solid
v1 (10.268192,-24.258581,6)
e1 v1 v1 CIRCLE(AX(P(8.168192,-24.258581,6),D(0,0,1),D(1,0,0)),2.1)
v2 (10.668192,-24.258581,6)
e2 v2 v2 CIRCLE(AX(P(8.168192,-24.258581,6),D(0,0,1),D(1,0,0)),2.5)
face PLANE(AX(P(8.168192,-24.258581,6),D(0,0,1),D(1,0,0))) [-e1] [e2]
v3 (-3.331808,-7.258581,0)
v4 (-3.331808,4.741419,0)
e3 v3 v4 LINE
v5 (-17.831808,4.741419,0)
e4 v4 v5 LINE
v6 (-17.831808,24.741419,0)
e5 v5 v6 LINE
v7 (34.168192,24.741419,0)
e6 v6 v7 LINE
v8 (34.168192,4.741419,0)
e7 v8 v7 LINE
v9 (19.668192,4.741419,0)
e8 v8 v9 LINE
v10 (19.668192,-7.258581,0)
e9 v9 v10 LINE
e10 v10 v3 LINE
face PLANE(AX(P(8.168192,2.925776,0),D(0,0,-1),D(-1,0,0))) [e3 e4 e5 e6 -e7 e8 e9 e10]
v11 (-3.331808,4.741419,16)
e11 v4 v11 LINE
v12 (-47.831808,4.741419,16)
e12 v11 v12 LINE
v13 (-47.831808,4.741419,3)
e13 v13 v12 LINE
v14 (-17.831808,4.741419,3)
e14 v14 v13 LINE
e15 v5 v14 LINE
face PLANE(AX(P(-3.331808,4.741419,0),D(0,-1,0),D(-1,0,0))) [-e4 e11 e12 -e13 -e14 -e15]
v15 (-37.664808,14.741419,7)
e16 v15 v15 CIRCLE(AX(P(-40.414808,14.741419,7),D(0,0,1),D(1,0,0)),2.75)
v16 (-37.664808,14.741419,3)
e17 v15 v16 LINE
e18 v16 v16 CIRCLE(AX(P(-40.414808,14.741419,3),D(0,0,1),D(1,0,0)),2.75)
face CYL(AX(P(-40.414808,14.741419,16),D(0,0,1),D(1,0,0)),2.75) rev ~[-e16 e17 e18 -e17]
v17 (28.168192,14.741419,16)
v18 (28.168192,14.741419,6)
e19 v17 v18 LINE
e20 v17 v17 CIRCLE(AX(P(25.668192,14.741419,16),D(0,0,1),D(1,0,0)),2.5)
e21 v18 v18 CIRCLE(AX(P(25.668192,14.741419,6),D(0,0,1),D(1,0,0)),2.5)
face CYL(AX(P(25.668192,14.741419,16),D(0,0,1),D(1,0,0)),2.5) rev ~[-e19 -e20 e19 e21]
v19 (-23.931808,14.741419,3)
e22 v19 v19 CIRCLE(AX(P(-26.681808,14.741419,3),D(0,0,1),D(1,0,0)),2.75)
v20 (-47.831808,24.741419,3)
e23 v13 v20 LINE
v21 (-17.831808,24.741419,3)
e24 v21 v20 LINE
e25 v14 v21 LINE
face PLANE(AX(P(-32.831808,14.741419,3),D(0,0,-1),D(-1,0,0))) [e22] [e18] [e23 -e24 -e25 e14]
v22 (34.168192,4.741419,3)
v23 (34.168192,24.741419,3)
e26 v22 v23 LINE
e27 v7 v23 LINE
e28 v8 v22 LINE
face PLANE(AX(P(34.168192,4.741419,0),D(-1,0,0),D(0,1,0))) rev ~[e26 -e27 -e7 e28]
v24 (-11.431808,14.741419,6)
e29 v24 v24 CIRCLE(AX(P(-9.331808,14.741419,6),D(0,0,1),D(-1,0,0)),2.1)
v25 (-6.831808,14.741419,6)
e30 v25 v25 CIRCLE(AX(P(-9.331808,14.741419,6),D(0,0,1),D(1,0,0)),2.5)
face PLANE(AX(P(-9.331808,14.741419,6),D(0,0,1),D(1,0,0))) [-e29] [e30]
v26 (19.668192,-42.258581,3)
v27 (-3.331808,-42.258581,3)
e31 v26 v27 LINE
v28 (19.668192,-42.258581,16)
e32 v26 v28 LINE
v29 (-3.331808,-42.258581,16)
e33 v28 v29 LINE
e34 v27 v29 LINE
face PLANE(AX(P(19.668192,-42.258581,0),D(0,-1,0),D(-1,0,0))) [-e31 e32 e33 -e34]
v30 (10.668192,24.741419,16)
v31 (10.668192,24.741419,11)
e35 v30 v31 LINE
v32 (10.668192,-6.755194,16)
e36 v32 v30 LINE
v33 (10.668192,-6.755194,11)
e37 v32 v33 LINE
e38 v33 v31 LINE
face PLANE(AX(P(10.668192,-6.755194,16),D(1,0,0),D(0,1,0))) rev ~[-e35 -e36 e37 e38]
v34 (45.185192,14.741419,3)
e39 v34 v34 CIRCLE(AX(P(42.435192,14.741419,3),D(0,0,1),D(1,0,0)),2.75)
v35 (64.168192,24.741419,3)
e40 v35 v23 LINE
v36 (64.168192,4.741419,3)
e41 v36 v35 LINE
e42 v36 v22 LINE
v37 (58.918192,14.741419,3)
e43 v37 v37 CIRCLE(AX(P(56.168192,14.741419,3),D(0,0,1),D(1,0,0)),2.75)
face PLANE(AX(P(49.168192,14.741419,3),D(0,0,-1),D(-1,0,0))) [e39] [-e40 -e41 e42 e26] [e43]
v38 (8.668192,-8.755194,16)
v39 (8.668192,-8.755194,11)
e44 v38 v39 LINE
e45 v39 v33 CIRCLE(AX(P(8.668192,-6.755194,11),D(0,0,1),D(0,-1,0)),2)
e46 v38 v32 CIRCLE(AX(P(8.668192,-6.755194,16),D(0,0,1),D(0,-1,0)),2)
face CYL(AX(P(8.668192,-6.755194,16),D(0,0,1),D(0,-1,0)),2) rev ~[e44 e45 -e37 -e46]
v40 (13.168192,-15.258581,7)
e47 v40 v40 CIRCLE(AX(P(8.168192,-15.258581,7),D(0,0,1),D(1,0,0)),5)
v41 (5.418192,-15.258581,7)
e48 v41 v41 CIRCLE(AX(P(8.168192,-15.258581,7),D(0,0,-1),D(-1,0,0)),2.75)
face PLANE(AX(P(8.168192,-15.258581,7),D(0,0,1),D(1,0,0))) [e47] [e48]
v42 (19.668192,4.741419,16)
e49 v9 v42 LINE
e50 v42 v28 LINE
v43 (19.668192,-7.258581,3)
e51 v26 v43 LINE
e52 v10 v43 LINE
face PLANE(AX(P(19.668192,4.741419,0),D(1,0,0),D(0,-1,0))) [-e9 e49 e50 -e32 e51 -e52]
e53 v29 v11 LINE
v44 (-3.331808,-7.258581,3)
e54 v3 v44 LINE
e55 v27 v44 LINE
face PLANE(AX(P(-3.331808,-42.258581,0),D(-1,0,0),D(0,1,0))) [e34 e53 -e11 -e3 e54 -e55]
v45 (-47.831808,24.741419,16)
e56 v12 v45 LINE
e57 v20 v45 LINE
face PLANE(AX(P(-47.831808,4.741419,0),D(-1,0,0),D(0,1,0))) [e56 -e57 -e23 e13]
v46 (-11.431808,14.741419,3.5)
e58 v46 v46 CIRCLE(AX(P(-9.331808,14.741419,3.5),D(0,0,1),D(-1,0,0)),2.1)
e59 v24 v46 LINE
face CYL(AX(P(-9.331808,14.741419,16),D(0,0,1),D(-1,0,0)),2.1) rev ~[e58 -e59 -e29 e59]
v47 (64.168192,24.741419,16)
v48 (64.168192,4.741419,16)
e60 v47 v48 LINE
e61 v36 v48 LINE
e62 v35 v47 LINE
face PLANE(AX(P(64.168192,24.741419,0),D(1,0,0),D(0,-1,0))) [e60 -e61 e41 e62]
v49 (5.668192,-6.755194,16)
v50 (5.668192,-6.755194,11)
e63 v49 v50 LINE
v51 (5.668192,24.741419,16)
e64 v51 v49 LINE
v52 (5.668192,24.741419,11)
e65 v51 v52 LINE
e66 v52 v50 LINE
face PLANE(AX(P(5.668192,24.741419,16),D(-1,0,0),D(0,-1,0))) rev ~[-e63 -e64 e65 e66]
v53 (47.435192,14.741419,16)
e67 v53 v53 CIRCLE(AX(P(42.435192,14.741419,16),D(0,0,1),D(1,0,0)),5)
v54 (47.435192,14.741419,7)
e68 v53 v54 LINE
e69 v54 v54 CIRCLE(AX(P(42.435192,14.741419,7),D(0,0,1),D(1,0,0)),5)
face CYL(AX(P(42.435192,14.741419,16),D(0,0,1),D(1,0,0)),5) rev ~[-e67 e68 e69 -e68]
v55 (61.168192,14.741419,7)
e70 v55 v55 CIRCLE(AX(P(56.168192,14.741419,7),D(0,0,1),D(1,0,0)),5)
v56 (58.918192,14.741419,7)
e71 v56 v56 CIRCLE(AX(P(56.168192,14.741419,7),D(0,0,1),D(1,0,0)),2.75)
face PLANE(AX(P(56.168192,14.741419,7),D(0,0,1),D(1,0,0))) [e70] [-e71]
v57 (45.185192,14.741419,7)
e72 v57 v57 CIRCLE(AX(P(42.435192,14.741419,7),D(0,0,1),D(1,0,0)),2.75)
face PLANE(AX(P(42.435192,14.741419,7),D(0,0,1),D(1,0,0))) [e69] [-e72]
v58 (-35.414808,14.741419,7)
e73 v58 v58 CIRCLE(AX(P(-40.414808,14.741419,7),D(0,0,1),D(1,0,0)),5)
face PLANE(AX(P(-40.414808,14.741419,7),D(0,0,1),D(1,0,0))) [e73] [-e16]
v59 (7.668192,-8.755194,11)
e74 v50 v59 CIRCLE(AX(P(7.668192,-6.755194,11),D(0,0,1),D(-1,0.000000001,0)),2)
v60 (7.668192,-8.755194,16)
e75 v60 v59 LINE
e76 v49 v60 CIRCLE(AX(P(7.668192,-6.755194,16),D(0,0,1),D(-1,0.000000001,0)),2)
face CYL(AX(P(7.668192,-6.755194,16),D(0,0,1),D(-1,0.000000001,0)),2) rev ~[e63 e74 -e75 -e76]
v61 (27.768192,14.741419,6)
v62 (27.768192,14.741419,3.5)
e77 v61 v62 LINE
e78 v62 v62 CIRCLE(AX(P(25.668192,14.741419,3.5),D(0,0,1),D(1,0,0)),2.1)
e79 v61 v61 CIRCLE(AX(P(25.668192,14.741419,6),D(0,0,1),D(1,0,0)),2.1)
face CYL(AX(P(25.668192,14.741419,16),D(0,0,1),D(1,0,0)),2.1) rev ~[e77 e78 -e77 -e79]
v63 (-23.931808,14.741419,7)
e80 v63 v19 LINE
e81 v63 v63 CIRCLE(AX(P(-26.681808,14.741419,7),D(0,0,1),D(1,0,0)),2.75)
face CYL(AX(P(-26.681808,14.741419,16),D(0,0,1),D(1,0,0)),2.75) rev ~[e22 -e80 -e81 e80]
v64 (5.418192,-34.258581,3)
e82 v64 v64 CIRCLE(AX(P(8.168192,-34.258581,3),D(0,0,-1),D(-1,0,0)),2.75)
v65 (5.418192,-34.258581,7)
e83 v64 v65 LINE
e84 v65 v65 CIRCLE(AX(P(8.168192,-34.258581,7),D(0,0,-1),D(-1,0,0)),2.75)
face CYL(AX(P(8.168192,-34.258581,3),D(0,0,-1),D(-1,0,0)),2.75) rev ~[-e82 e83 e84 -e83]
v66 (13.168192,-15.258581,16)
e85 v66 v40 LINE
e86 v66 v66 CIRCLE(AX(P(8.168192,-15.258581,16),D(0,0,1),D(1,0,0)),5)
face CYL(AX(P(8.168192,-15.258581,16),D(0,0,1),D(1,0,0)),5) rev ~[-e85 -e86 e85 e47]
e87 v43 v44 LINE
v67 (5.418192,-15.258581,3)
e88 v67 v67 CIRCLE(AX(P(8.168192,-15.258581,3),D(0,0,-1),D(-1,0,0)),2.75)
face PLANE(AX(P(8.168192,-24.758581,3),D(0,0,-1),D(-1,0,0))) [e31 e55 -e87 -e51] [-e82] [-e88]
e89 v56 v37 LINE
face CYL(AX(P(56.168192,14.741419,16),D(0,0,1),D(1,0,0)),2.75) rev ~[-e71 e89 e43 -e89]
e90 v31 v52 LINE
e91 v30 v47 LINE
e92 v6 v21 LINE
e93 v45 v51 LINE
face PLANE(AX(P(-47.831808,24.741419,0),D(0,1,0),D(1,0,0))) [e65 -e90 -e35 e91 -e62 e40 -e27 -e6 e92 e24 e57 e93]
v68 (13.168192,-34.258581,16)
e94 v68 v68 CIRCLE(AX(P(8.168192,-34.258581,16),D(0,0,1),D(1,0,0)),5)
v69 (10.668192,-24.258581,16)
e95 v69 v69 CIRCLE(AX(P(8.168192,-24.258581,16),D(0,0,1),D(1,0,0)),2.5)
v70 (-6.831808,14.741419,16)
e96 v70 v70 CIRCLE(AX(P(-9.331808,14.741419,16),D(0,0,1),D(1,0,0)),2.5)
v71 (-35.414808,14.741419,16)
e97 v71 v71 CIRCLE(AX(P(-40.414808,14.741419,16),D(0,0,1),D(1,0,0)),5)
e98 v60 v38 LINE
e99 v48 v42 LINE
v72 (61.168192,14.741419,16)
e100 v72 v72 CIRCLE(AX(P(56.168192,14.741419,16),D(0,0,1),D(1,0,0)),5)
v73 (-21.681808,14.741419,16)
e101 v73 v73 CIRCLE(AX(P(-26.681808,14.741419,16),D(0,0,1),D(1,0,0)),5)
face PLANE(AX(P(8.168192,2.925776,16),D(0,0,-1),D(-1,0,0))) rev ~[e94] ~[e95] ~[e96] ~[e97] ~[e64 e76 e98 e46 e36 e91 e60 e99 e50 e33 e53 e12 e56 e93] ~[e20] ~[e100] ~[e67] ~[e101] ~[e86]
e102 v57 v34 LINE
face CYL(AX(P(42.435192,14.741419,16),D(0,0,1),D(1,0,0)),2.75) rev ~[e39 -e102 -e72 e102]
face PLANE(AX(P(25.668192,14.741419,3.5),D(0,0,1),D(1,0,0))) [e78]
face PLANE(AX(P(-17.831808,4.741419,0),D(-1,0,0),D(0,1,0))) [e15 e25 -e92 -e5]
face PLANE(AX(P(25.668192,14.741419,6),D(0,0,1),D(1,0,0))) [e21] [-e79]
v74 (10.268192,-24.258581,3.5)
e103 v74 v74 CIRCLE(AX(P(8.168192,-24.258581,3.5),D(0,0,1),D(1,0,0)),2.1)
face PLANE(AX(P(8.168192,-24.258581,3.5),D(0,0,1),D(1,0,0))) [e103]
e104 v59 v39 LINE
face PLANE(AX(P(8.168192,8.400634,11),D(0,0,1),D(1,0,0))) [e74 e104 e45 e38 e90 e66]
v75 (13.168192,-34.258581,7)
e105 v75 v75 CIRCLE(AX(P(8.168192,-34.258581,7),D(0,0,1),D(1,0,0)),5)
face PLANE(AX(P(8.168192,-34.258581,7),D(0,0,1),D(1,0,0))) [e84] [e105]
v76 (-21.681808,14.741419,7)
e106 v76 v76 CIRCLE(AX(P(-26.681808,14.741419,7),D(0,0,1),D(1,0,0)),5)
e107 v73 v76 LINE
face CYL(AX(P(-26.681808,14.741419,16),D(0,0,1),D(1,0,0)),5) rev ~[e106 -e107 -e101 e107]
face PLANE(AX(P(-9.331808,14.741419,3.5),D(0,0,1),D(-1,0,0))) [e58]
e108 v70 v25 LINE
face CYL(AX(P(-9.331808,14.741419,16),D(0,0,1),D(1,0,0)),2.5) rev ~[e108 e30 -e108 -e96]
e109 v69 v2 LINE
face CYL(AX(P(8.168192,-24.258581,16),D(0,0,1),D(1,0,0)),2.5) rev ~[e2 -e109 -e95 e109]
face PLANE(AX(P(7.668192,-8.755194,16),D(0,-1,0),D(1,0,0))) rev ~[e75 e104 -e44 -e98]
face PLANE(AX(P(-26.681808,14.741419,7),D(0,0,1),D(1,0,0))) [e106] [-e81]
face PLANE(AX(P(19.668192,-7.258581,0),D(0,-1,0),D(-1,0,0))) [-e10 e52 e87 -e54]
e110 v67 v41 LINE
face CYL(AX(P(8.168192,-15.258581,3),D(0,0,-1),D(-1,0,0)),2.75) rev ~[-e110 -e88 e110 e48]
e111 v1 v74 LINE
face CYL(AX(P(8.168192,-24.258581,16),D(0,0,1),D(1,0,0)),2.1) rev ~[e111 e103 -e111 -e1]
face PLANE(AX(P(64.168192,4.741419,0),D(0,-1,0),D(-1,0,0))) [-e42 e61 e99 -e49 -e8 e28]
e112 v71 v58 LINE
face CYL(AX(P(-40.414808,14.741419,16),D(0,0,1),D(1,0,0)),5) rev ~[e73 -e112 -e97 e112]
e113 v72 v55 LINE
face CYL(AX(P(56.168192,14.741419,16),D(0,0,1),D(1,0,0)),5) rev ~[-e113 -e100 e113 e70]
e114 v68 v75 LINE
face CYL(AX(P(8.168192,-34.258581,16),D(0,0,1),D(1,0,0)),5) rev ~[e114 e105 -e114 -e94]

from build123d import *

# Parameters (mm, degrees)
EXTRUDE_1_DEPTH     = 16
SKETCH_2_W          = 30
SKETCH_2_H          = 20
SKETCH_2_W_2        = 23
SKETCH_2_H_2        = 35
CUT_EXTRUDE_1_DEPTH = 3
CUT_EXTRUDE_2_DEPTH = 5
CUT_EXTRUDE_3_REACH = 80.481
SKETCH_4_R          = 2.75
CUT_EXTRUDE_4_REACH = 79.925
SKETCH_5_R          = 2.75
SKETCH_6_R          = 5
CUT_EXTRUDE_5_DEPTH = 9
SKETCH_7_R          = 2.1
CUT_EXTRUDE_6_DEPTH = 12.5
SKETCH_8_R          = 2.5
CUT_EXTRUDE_7_DEPTH = 10


with BuildPart() as part:
    # 草图1 → 凸台-拉伸1 (new body)
    with BuildSketch(Plane.XY):
        Polygon((-47.83180778, 24.741418764), (64.16819222, 24.741418764), (64.16819222, 4.741418764), (19.66819222, 4.741418764), (19.66819222, -42.258581236), (-3.33180778, -42.258581236), (-3.33180778, 4.741418764), (-47.83180778, 4.741418764), align=None)
    extrude(amount=EXTRUDE_1_DEPTH)

    # 草图2 → 切除-拉伸1 (cut)
    with BuildSketch(Plane(origin=(0, 0, 0), x_dir=(-1, 0, 0), z_dir=(0, 0, -1))):
        with Locations((-49.16819222, 14.741418764)):
            Rectangle(SKETCH_2_W, SKETCH_2_H)
        with Locations((-8.16819222, -24.758581236)):
            Rectangle(SKETCH_2_W_2, SKETCH_2_H_2)
        with Locations((32.83180778, 14.741418764)):
            Rectangle(SKETCH_2_W, SKETCH_2_H)
    extrude(amount=-CUT_EXTRUDE_1_DEPTH, mode=Mode.SUBTRACT)

    # 草图3 → 切除-拉伸2 (cut)
    with BuildSketch(Plane.XY.offset(16)):
        with BuildLine():
            Line((10.66819222, 24.741418764), (5.66819222, 24.741418764))
            Line((5.66819222, 24.741418764), (5.66819222, -6.755194133))
            ThreePointArc((5.66819222, -6.755194133), (6.253978657, -8.169407696), (7.66819222, -8.755194133))
            Line((7.66819222, -8.755194133), (8.66819222, -8.755194133))
            ThreePointArc((8.66819222, -8.755194133), (10.082405782, -8.169407696), (10.66819222, -6.755194133))
            Line((10.66819222, -6.755194133), (10.66819222, 24.741418764))
        make_face()
    extrude(amount=-CUT_EXTRUDE_2_DEPTH, mode=Mode.SUBTRACT)

    # 草图4 → 切除-拉伸3 (cut, up to next)
    with BuildSketch(Plane.XY.offset(16), mode=Mode.PRIVATE) as cut_extrude_3_sk1:
        with Locations((56.16819222, 14.741418764)):
            Circle(SKETCH_4_R)
    cut_extrude_3_tool1 = extrude(cut_extrude_3_sk1.sketch, amount=-CUT_EXTRUDE_3_REACH, mode=Mode.PRIVATE) & part.part
    # 草图4 → 切除-拉伸3 (cut, up to next)
    with BuildSketch(Plane.XY.offset(16), mode=Mode.PRIVATE) as cut_extrude_3_sk2:
        with Locations((42.43519222, 14.741418764)):
            Circle(SKETCH_4_R)
    cut_extrude_3_tool2 = extrude(cut_extrude_3_sk2.sketch, amount=-CUT_EXTRUDE_3_REACH, mode=Mode.PRIVATE) & part.part
    # 草图4 → 切除-拉伸3 (cut, up to next)
    with BuildSketch(Plane.XY.offset(16), mode=Mode.PRIVATE) as cut_extrude_3_sk3:
        with Locations((-26.68180778, 14.741418764)):
            Circle(SKETCH_4_R)
    cut_extrude_3_tool3 = extrude(cut_extrude_3_sk3.sketch, amount=-CUT_EXTRUDE_3_REACH, mode=Mode.PRIVATE) & part.part
    # 草图4 → 切除-拉伸3 (cut, up to next)
    with BuildSketch(Plane.XY.offset(16), mode=Mode.PRIVATE) as cut_extrude_3_sk4:
        with Locations((-40.41480778, 14.741418764)):
            Circle(SKETCH_4_R)
    cut_extrude_3_tool4 = extrude(cut_extrude_3_sk4.sketch, amount=-CUT_EXTRUDE_3_REACH, mode=Mode.PRIVATE) & part.part
    add(cut_extrude_3_tool1.solids().sort_by_distance((56.168192, 14.741419, 16))[0], mode=Mode.SUBTRACT)
    add(cut_extrude_3_tool2.solids().sort_by_distance((42.435192, 14.741419, 16))[0], mode=Mode.SUBTRACT)
    add(cut_extrude_3_tool3.solids().sort_by_distance((-26.681808, 14.741419, 16))[0], mode=Mode.SUBTRACT)
    add(cut_extrude_3_tool4.solids().sort_by_distance((-40.414808, 14.741419, 16))[0], mode=Mode.SUBTRACT)

    # 草图5 → 切除-拉伸4 (cut, up to next)
    with BuildSketch(Plane(origin=(0, 0, 3), x_dir=(-1, 0, 0), z_dir=(0, 0, -1)), mode=Mode.PRIVATE) as cut_extrude_4_sk1:
        with Locations((-8.16819222, -15.258581236)):
            Circle(SKETCH_5_R)
    cut_extrude_4_tool1 = extrude(cut_extrude_4_sk1.sketch, amount=-CUT_EXTRUDE_4_REACH, mode=Mode.PRIVATE) & part.part
    # 草图5 → 切除-拉伸4 (cut, up to next)
    with BuildSketch(Plane(origin=(0, 0, 3), x_dir=(-1, 0, 0), z_dir=(0, 0, -1)), mode=Mode.PRIVATE) as cut_extrude_4_sk2:
        with Locations((-8.16819222, -34.258581236)):
            Circle(SKETCH_5_R)
    cut_extrude_4_tool2 = extrude(cut_extrude_4_sk2.sketch, amount=-CUT_EXTRUDE_4_REACH, mode=Mode.PRIVATE) & part.part
    add(cut_extrude_4_tool1.solids().sort_by_distance((8.168192, -15.258581, 3))[0], mode=Mode.SUBTRACT)
    add(cut_extrude_4_tool2.solids().sort_by_distance((8.168192, -34.258581, 3))[0], mode=Mode.SUBTRACT)

    # 草图6 → 切除-拉伸5 (cut)
    with BuildSketch(Plane.XY.offset(16)):
        with Locations((-40.41480778, 14.741418764)):
            Circle(SKETCH_6_R)
        with Locations((-26.68180778, 14.741418764)):
            Circle(SKETCH_6_R)
        with Locations((42.43519222, 14.741418764)):
            Circle(SKETCH_6_R)
        with Locations((56.16819222, 14.741418764)):
            Circle(SKETCH_6_R)
        with Locations((8.16819222, -15.258581236)):
            Circle(SKETCH_6_R)
        with Locations((8.16819222, -34.258581236)):
            Circle(SKETCH_6_R)
    extrude(amount=-CUT_EXTRUDE_5_DEPTH, mode=Mode.SUBTRACT)

    # 草图7 → 切除-拉伸6 (cut)
    with BuildSketch(Plane.XY.offset(16)):
        with Locations((25.66819222, 14.741418764)):
            Circle(SKETCH_7_R)
        with Locations(Location((-9.33180778, 14.741418764, 0), (0, 0, 180))):
            Circle(SKETCH_7_R)
        with Locations((8.16819222, -24.258581236)):
            Circle(SKETCH_7_R)
    extrude(amount=-CUT_EXTRUDE_6_DEPTH, mode=Mode.SUBTRACT)

    # 草图8 → 切除-拉伸7 (cut)
    with BuildSketch(Plane.XY.offset(16)):
        with Locations((-9.33180778, 14.741418764)):
            Circle(SKETCH_8_R)
        with Locations((25.66819222, 14.741418764)):
            Circle(SKETCH_8_R)
        with Locations((8.16819222, -24.258581236)):
            Circle(SKETCH_8_R)
    extrude(amount=-CUT_EXTRUDE_7_DEPTH, mode=Mode.SUBTRACT)


solid = part.part
